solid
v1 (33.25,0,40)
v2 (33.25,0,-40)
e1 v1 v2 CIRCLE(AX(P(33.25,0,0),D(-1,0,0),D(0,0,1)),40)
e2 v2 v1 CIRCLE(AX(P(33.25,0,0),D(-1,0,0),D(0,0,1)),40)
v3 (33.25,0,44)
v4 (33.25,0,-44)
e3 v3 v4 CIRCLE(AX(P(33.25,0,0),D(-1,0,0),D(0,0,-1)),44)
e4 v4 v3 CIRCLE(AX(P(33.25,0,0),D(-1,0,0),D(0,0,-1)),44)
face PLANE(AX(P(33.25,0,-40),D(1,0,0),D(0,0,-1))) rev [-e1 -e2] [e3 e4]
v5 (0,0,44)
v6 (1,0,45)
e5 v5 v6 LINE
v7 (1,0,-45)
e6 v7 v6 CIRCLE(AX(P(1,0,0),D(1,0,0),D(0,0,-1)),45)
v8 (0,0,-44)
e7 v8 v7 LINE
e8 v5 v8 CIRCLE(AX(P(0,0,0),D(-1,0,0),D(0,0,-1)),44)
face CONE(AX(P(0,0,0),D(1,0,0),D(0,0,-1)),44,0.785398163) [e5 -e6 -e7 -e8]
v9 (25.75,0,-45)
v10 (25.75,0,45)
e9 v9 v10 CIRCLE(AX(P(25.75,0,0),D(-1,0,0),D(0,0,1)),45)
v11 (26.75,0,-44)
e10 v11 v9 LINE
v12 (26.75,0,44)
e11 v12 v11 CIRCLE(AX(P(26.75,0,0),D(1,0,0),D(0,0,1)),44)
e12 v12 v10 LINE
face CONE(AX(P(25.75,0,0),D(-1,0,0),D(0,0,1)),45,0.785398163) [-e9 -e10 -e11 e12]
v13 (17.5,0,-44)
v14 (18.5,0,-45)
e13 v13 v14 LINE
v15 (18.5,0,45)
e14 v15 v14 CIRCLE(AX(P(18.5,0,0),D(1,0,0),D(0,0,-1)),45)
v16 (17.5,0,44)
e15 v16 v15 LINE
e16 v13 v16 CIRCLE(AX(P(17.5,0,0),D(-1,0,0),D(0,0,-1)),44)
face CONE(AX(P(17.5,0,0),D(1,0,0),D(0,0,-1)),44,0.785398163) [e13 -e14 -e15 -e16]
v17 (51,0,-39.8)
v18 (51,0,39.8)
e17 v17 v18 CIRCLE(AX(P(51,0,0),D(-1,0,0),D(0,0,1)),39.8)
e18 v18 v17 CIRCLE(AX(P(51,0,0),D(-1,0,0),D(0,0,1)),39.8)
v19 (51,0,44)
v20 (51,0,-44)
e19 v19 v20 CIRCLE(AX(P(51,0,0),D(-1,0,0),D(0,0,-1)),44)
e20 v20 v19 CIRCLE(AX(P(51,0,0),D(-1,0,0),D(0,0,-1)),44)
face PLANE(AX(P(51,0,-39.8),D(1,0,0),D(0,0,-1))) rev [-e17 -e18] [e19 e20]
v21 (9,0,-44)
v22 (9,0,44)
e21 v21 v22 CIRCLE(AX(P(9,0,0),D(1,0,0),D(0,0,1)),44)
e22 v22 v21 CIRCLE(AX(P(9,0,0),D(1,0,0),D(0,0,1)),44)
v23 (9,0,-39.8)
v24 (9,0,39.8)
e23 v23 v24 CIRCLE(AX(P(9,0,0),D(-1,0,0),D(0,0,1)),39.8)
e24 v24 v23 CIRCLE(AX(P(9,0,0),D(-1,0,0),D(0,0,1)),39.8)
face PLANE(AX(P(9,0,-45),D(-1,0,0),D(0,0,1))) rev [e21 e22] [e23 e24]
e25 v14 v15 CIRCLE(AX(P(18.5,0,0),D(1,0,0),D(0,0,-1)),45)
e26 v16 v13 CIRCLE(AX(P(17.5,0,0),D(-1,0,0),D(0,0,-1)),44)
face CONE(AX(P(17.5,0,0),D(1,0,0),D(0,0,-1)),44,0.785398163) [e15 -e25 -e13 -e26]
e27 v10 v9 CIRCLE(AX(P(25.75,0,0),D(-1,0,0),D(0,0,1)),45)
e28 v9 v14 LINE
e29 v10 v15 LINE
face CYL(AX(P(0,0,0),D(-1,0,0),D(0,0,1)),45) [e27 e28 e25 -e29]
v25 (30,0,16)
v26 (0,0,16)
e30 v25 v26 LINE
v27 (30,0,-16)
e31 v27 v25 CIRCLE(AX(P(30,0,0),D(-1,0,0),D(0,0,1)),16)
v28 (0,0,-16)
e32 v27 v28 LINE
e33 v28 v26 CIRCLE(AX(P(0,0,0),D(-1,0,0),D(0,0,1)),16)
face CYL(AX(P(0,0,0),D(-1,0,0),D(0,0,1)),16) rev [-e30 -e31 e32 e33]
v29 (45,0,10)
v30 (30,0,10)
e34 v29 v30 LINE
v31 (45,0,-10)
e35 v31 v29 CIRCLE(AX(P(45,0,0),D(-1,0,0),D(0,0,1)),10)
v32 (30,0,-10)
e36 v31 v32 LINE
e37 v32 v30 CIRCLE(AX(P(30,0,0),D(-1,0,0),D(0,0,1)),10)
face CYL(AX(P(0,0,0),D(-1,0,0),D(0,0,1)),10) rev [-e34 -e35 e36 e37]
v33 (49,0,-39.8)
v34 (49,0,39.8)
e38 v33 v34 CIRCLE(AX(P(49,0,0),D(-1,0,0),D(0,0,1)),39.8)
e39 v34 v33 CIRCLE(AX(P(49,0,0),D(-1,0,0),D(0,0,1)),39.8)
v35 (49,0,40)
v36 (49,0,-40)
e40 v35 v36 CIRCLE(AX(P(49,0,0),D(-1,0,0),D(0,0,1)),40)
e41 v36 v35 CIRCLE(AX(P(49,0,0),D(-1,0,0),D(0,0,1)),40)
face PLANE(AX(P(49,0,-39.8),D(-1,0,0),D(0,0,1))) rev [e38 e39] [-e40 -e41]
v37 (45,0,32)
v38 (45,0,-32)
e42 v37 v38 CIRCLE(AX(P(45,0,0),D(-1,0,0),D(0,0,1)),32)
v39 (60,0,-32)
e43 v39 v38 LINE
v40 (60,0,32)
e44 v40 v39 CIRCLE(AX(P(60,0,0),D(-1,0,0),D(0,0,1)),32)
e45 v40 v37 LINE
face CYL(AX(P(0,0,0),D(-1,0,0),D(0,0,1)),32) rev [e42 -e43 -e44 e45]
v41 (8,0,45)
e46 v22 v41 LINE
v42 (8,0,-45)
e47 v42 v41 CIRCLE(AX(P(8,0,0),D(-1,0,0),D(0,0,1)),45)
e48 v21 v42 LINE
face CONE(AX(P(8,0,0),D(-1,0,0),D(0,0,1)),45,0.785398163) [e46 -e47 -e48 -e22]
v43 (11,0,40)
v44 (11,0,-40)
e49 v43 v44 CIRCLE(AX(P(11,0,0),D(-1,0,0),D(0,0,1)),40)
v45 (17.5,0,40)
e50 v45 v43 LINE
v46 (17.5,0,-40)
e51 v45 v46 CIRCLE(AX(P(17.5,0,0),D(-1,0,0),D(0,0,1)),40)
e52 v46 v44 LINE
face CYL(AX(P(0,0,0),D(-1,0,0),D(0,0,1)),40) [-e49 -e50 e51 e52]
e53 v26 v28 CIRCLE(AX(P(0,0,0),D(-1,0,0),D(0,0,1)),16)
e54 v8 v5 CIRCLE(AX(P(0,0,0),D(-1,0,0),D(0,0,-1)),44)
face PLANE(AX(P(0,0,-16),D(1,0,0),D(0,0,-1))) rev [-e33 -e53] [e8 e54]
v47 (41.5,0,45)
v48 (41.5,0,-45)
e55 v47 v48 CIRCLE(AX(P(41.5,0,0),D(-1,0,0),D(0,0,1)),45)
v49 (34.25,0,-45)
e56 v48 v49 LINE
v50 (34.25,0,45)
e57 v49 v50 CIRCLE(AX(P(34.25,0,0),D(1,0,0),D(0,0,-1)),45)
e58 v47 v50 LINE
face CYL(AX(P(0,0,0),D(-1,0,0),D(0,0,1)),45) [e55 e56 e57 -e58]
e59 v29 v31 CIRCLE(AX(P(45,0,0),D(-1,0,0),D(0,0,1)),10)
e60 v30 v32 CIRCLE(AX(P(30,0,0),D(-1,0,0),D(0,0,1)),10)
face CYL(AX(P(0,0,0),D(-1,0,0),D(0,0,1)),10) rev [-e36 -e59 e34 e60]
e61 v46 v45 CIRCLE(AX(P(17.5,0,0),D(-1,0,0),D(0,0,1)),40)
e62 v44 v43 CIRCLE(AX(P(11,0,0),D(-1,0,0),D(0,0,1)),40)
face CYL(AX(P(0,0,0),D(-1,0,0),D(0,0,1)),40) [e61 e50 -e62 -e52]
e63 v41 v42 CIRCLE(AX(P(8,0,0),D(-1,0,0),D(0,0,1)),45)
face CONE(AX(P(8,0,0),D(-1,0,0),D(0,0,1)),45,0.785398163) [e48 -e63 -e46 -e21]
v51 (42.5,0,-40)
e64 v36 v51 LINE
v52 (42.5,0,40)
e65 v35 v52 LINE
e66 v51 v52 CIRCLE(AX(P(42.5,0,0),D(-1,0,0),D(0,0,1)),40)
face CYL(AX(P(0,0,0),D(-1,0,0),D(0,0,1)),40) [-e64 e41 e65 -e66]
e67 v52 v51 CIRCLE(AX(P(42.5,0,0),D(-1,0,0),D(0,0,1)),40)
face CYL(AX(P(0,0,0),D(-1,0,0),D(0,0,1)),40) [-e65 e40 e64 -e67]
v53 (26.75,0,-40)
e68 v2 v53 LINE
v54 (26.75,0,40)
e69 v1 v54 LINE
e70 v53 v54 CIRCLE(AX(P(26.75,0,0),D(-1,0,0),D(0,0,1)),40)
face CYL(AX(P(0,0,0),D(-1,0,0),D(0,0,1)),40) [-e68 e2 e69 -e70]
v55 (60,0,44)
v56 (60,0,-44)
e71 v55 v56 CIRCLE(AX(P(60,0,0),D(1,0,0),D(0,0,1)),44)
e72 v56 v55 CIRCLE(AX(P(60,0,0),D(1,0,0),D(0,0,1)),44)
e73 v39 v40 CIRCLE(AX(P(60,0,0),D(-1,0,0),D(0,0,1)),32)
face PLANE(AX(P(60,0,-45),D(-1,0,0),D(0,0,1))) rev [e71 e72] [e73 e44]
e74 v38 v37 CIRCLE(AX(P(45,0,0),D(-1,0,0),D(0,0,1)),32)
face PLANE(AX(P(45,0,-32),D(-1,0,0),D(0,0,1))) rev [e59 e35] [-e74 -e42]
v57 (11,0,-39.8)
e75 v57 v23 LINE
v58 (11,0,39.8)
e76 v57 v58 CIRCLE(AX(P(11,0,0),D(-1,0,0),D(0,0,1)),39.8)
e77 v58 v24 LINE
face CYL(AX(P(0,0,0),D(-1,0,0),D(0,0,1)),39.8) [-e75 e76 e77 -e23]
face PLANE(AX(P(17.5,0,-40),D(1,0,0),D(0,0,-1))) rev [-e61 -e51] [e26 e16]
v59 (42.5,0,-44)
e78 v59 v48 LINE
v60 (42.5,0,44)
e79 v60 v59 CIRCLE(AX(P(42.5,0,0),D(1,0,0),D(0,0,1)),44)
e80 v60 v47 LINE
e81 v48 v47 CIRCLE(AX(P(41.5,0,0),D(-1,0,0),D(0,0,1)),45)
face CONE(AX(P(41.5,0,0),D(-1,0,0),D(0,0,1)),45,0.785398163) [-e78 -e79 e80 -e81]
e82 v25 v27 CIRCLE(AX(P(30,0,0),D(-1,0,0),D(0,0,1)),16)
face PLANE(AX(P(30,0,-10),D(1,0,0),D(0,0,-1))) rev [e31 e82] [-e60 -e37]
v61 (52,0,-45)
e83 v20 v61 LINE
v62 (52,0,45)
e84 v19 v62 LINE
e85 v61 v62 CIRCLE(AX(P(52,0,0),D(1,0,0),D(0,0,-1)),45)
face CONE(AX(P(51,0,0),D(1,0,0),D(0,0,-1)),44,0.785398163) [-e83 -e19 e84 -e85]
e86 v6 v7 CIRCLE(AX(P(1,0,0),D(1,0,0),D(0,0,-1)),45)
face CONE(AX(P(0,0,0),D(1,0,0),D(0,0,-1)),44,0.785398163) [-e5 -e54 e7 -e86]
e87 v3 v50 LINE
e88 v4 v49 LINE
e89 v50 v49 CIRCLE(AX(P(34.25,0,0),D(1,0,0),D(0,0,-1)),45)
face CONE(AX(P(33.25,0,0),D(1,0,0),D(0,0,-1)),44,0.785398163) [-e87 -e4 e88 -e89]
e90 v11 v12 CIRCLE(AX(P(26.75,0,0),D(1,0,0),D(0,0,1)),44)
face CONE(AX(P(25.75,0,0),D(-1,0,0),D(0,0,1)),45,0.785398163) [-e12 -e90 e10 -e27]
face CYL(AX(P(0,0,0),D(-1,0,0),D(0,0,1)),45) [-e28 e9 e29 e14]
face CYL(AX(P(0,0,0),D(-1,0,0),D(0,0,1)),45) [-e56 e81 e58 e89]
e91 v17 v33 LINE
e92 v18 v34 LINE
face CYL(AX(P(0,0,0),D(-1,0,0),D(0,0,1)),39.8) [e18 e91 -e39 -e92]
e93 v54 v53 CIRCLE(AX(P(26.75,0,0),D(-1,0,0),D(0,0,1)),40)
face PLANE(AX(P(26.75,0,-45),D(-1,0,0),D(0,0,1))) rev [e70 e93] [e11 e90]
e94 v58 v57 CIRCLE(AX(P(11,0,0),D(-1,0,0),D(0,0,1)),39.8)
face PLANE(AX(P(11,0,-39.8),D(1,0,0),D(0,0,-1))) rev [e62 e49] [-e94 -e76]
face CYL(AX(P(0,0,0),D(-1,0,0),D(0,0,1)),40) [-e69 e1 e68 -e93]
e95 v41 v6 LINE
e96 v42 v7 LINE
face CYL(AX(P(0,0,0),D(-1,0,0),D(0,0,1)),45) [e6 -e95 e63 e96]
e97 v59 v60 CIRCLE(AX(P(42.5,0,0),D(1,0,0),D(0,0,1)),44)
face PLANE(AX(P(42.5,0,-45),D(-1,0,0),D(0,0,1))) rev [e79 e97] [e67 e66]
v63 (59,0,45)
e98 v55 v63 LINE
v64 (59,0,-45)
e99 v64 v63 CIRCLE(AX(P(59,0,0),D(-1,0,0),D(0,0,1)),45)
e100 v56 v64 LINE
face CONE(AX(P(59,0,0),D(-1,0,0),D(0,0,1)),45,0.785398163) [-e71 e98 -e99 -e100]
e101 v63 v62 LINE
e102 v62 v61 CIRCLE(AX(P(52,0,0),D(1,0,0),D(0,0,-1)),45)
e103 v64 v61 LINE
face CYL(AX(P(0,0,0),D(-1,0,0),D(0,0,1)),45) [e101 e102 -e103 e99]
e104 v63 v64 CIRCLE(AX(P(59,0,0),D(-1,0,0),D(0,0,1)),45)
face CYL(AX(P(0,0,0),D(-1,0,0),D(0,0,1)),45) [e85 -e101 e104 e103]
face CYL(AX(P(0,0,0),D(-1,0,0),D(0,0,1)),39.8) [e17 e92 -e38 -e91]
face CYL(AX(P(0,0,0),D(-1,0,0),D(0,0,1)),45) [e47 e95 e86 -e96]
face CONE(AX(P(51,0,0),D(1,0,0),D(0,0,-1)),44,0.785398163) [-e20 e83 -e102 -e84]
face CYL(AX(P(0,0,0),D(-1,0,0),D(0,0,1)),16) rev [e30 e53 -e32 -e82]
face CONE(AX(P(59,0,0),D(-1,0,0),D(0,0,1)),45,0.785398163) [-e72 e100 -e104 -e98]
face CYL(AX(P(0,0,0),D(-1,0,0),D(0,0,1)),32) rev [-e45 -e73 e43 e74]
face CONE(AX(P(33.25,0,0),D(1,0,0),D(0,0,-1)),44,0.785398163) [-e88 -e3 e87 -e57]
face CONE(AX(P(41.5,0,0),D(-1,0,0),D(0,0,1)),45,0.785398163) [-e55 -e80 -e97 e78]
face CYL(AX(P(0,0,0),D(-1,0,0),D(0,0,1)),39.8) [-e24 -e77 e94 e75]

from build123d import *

# Parameters (mm, degrees)
CHAMFER_1_SIZE = 1


with BuildPart() as part:
    # 草图1 → 旋转1 (revolve)
    with BuildSketch(Plane(origin=(0, 0, 0), x_dir=(1, 0, 0), z_dir=(0, 1, 0)), mode=Mode.PRIVATE) as revolve_1_sk:
        Polygon((0, 16), (0, 45), (9, 45), (9, 39.8), (11, 39.8), (11, 40), (17.5, 40), (17.5, 45), (26.75, 45), (26.75, 40), (33.25, 40), (33.25, 45), (42.5, 45), (42.5, 40), (49, 40), (49, 39.8), (51, 39.8), (51, 45), (60, 45), (60, 32), (45, 32), (45, 10), (30, 10), (30, 16), align=None)
    revolve(revolve_1_sk.sketch.rotate(Axis((0, 0, 0), (1, 0, 0)), 180), axis=Axis((0, 0, 0), (1, 0, 0)))

    # 倒角1
    chamfer_1_edges = [part.edges().sort_by_distance(p)[0] for p in [
        (60, 0, -45),
        (51, 0, -45),
        (42.5, 0, -45),
        (33.25, 0, -45),
        (26.75, 0, -45),
        (17.5, 0, -45),
        (9, 0, -45),
        (0, 0, -45),
    ]]
    chamfer(chamfer_1_edges, length=CHAMFER_1_SIZE)


solid = part.part
